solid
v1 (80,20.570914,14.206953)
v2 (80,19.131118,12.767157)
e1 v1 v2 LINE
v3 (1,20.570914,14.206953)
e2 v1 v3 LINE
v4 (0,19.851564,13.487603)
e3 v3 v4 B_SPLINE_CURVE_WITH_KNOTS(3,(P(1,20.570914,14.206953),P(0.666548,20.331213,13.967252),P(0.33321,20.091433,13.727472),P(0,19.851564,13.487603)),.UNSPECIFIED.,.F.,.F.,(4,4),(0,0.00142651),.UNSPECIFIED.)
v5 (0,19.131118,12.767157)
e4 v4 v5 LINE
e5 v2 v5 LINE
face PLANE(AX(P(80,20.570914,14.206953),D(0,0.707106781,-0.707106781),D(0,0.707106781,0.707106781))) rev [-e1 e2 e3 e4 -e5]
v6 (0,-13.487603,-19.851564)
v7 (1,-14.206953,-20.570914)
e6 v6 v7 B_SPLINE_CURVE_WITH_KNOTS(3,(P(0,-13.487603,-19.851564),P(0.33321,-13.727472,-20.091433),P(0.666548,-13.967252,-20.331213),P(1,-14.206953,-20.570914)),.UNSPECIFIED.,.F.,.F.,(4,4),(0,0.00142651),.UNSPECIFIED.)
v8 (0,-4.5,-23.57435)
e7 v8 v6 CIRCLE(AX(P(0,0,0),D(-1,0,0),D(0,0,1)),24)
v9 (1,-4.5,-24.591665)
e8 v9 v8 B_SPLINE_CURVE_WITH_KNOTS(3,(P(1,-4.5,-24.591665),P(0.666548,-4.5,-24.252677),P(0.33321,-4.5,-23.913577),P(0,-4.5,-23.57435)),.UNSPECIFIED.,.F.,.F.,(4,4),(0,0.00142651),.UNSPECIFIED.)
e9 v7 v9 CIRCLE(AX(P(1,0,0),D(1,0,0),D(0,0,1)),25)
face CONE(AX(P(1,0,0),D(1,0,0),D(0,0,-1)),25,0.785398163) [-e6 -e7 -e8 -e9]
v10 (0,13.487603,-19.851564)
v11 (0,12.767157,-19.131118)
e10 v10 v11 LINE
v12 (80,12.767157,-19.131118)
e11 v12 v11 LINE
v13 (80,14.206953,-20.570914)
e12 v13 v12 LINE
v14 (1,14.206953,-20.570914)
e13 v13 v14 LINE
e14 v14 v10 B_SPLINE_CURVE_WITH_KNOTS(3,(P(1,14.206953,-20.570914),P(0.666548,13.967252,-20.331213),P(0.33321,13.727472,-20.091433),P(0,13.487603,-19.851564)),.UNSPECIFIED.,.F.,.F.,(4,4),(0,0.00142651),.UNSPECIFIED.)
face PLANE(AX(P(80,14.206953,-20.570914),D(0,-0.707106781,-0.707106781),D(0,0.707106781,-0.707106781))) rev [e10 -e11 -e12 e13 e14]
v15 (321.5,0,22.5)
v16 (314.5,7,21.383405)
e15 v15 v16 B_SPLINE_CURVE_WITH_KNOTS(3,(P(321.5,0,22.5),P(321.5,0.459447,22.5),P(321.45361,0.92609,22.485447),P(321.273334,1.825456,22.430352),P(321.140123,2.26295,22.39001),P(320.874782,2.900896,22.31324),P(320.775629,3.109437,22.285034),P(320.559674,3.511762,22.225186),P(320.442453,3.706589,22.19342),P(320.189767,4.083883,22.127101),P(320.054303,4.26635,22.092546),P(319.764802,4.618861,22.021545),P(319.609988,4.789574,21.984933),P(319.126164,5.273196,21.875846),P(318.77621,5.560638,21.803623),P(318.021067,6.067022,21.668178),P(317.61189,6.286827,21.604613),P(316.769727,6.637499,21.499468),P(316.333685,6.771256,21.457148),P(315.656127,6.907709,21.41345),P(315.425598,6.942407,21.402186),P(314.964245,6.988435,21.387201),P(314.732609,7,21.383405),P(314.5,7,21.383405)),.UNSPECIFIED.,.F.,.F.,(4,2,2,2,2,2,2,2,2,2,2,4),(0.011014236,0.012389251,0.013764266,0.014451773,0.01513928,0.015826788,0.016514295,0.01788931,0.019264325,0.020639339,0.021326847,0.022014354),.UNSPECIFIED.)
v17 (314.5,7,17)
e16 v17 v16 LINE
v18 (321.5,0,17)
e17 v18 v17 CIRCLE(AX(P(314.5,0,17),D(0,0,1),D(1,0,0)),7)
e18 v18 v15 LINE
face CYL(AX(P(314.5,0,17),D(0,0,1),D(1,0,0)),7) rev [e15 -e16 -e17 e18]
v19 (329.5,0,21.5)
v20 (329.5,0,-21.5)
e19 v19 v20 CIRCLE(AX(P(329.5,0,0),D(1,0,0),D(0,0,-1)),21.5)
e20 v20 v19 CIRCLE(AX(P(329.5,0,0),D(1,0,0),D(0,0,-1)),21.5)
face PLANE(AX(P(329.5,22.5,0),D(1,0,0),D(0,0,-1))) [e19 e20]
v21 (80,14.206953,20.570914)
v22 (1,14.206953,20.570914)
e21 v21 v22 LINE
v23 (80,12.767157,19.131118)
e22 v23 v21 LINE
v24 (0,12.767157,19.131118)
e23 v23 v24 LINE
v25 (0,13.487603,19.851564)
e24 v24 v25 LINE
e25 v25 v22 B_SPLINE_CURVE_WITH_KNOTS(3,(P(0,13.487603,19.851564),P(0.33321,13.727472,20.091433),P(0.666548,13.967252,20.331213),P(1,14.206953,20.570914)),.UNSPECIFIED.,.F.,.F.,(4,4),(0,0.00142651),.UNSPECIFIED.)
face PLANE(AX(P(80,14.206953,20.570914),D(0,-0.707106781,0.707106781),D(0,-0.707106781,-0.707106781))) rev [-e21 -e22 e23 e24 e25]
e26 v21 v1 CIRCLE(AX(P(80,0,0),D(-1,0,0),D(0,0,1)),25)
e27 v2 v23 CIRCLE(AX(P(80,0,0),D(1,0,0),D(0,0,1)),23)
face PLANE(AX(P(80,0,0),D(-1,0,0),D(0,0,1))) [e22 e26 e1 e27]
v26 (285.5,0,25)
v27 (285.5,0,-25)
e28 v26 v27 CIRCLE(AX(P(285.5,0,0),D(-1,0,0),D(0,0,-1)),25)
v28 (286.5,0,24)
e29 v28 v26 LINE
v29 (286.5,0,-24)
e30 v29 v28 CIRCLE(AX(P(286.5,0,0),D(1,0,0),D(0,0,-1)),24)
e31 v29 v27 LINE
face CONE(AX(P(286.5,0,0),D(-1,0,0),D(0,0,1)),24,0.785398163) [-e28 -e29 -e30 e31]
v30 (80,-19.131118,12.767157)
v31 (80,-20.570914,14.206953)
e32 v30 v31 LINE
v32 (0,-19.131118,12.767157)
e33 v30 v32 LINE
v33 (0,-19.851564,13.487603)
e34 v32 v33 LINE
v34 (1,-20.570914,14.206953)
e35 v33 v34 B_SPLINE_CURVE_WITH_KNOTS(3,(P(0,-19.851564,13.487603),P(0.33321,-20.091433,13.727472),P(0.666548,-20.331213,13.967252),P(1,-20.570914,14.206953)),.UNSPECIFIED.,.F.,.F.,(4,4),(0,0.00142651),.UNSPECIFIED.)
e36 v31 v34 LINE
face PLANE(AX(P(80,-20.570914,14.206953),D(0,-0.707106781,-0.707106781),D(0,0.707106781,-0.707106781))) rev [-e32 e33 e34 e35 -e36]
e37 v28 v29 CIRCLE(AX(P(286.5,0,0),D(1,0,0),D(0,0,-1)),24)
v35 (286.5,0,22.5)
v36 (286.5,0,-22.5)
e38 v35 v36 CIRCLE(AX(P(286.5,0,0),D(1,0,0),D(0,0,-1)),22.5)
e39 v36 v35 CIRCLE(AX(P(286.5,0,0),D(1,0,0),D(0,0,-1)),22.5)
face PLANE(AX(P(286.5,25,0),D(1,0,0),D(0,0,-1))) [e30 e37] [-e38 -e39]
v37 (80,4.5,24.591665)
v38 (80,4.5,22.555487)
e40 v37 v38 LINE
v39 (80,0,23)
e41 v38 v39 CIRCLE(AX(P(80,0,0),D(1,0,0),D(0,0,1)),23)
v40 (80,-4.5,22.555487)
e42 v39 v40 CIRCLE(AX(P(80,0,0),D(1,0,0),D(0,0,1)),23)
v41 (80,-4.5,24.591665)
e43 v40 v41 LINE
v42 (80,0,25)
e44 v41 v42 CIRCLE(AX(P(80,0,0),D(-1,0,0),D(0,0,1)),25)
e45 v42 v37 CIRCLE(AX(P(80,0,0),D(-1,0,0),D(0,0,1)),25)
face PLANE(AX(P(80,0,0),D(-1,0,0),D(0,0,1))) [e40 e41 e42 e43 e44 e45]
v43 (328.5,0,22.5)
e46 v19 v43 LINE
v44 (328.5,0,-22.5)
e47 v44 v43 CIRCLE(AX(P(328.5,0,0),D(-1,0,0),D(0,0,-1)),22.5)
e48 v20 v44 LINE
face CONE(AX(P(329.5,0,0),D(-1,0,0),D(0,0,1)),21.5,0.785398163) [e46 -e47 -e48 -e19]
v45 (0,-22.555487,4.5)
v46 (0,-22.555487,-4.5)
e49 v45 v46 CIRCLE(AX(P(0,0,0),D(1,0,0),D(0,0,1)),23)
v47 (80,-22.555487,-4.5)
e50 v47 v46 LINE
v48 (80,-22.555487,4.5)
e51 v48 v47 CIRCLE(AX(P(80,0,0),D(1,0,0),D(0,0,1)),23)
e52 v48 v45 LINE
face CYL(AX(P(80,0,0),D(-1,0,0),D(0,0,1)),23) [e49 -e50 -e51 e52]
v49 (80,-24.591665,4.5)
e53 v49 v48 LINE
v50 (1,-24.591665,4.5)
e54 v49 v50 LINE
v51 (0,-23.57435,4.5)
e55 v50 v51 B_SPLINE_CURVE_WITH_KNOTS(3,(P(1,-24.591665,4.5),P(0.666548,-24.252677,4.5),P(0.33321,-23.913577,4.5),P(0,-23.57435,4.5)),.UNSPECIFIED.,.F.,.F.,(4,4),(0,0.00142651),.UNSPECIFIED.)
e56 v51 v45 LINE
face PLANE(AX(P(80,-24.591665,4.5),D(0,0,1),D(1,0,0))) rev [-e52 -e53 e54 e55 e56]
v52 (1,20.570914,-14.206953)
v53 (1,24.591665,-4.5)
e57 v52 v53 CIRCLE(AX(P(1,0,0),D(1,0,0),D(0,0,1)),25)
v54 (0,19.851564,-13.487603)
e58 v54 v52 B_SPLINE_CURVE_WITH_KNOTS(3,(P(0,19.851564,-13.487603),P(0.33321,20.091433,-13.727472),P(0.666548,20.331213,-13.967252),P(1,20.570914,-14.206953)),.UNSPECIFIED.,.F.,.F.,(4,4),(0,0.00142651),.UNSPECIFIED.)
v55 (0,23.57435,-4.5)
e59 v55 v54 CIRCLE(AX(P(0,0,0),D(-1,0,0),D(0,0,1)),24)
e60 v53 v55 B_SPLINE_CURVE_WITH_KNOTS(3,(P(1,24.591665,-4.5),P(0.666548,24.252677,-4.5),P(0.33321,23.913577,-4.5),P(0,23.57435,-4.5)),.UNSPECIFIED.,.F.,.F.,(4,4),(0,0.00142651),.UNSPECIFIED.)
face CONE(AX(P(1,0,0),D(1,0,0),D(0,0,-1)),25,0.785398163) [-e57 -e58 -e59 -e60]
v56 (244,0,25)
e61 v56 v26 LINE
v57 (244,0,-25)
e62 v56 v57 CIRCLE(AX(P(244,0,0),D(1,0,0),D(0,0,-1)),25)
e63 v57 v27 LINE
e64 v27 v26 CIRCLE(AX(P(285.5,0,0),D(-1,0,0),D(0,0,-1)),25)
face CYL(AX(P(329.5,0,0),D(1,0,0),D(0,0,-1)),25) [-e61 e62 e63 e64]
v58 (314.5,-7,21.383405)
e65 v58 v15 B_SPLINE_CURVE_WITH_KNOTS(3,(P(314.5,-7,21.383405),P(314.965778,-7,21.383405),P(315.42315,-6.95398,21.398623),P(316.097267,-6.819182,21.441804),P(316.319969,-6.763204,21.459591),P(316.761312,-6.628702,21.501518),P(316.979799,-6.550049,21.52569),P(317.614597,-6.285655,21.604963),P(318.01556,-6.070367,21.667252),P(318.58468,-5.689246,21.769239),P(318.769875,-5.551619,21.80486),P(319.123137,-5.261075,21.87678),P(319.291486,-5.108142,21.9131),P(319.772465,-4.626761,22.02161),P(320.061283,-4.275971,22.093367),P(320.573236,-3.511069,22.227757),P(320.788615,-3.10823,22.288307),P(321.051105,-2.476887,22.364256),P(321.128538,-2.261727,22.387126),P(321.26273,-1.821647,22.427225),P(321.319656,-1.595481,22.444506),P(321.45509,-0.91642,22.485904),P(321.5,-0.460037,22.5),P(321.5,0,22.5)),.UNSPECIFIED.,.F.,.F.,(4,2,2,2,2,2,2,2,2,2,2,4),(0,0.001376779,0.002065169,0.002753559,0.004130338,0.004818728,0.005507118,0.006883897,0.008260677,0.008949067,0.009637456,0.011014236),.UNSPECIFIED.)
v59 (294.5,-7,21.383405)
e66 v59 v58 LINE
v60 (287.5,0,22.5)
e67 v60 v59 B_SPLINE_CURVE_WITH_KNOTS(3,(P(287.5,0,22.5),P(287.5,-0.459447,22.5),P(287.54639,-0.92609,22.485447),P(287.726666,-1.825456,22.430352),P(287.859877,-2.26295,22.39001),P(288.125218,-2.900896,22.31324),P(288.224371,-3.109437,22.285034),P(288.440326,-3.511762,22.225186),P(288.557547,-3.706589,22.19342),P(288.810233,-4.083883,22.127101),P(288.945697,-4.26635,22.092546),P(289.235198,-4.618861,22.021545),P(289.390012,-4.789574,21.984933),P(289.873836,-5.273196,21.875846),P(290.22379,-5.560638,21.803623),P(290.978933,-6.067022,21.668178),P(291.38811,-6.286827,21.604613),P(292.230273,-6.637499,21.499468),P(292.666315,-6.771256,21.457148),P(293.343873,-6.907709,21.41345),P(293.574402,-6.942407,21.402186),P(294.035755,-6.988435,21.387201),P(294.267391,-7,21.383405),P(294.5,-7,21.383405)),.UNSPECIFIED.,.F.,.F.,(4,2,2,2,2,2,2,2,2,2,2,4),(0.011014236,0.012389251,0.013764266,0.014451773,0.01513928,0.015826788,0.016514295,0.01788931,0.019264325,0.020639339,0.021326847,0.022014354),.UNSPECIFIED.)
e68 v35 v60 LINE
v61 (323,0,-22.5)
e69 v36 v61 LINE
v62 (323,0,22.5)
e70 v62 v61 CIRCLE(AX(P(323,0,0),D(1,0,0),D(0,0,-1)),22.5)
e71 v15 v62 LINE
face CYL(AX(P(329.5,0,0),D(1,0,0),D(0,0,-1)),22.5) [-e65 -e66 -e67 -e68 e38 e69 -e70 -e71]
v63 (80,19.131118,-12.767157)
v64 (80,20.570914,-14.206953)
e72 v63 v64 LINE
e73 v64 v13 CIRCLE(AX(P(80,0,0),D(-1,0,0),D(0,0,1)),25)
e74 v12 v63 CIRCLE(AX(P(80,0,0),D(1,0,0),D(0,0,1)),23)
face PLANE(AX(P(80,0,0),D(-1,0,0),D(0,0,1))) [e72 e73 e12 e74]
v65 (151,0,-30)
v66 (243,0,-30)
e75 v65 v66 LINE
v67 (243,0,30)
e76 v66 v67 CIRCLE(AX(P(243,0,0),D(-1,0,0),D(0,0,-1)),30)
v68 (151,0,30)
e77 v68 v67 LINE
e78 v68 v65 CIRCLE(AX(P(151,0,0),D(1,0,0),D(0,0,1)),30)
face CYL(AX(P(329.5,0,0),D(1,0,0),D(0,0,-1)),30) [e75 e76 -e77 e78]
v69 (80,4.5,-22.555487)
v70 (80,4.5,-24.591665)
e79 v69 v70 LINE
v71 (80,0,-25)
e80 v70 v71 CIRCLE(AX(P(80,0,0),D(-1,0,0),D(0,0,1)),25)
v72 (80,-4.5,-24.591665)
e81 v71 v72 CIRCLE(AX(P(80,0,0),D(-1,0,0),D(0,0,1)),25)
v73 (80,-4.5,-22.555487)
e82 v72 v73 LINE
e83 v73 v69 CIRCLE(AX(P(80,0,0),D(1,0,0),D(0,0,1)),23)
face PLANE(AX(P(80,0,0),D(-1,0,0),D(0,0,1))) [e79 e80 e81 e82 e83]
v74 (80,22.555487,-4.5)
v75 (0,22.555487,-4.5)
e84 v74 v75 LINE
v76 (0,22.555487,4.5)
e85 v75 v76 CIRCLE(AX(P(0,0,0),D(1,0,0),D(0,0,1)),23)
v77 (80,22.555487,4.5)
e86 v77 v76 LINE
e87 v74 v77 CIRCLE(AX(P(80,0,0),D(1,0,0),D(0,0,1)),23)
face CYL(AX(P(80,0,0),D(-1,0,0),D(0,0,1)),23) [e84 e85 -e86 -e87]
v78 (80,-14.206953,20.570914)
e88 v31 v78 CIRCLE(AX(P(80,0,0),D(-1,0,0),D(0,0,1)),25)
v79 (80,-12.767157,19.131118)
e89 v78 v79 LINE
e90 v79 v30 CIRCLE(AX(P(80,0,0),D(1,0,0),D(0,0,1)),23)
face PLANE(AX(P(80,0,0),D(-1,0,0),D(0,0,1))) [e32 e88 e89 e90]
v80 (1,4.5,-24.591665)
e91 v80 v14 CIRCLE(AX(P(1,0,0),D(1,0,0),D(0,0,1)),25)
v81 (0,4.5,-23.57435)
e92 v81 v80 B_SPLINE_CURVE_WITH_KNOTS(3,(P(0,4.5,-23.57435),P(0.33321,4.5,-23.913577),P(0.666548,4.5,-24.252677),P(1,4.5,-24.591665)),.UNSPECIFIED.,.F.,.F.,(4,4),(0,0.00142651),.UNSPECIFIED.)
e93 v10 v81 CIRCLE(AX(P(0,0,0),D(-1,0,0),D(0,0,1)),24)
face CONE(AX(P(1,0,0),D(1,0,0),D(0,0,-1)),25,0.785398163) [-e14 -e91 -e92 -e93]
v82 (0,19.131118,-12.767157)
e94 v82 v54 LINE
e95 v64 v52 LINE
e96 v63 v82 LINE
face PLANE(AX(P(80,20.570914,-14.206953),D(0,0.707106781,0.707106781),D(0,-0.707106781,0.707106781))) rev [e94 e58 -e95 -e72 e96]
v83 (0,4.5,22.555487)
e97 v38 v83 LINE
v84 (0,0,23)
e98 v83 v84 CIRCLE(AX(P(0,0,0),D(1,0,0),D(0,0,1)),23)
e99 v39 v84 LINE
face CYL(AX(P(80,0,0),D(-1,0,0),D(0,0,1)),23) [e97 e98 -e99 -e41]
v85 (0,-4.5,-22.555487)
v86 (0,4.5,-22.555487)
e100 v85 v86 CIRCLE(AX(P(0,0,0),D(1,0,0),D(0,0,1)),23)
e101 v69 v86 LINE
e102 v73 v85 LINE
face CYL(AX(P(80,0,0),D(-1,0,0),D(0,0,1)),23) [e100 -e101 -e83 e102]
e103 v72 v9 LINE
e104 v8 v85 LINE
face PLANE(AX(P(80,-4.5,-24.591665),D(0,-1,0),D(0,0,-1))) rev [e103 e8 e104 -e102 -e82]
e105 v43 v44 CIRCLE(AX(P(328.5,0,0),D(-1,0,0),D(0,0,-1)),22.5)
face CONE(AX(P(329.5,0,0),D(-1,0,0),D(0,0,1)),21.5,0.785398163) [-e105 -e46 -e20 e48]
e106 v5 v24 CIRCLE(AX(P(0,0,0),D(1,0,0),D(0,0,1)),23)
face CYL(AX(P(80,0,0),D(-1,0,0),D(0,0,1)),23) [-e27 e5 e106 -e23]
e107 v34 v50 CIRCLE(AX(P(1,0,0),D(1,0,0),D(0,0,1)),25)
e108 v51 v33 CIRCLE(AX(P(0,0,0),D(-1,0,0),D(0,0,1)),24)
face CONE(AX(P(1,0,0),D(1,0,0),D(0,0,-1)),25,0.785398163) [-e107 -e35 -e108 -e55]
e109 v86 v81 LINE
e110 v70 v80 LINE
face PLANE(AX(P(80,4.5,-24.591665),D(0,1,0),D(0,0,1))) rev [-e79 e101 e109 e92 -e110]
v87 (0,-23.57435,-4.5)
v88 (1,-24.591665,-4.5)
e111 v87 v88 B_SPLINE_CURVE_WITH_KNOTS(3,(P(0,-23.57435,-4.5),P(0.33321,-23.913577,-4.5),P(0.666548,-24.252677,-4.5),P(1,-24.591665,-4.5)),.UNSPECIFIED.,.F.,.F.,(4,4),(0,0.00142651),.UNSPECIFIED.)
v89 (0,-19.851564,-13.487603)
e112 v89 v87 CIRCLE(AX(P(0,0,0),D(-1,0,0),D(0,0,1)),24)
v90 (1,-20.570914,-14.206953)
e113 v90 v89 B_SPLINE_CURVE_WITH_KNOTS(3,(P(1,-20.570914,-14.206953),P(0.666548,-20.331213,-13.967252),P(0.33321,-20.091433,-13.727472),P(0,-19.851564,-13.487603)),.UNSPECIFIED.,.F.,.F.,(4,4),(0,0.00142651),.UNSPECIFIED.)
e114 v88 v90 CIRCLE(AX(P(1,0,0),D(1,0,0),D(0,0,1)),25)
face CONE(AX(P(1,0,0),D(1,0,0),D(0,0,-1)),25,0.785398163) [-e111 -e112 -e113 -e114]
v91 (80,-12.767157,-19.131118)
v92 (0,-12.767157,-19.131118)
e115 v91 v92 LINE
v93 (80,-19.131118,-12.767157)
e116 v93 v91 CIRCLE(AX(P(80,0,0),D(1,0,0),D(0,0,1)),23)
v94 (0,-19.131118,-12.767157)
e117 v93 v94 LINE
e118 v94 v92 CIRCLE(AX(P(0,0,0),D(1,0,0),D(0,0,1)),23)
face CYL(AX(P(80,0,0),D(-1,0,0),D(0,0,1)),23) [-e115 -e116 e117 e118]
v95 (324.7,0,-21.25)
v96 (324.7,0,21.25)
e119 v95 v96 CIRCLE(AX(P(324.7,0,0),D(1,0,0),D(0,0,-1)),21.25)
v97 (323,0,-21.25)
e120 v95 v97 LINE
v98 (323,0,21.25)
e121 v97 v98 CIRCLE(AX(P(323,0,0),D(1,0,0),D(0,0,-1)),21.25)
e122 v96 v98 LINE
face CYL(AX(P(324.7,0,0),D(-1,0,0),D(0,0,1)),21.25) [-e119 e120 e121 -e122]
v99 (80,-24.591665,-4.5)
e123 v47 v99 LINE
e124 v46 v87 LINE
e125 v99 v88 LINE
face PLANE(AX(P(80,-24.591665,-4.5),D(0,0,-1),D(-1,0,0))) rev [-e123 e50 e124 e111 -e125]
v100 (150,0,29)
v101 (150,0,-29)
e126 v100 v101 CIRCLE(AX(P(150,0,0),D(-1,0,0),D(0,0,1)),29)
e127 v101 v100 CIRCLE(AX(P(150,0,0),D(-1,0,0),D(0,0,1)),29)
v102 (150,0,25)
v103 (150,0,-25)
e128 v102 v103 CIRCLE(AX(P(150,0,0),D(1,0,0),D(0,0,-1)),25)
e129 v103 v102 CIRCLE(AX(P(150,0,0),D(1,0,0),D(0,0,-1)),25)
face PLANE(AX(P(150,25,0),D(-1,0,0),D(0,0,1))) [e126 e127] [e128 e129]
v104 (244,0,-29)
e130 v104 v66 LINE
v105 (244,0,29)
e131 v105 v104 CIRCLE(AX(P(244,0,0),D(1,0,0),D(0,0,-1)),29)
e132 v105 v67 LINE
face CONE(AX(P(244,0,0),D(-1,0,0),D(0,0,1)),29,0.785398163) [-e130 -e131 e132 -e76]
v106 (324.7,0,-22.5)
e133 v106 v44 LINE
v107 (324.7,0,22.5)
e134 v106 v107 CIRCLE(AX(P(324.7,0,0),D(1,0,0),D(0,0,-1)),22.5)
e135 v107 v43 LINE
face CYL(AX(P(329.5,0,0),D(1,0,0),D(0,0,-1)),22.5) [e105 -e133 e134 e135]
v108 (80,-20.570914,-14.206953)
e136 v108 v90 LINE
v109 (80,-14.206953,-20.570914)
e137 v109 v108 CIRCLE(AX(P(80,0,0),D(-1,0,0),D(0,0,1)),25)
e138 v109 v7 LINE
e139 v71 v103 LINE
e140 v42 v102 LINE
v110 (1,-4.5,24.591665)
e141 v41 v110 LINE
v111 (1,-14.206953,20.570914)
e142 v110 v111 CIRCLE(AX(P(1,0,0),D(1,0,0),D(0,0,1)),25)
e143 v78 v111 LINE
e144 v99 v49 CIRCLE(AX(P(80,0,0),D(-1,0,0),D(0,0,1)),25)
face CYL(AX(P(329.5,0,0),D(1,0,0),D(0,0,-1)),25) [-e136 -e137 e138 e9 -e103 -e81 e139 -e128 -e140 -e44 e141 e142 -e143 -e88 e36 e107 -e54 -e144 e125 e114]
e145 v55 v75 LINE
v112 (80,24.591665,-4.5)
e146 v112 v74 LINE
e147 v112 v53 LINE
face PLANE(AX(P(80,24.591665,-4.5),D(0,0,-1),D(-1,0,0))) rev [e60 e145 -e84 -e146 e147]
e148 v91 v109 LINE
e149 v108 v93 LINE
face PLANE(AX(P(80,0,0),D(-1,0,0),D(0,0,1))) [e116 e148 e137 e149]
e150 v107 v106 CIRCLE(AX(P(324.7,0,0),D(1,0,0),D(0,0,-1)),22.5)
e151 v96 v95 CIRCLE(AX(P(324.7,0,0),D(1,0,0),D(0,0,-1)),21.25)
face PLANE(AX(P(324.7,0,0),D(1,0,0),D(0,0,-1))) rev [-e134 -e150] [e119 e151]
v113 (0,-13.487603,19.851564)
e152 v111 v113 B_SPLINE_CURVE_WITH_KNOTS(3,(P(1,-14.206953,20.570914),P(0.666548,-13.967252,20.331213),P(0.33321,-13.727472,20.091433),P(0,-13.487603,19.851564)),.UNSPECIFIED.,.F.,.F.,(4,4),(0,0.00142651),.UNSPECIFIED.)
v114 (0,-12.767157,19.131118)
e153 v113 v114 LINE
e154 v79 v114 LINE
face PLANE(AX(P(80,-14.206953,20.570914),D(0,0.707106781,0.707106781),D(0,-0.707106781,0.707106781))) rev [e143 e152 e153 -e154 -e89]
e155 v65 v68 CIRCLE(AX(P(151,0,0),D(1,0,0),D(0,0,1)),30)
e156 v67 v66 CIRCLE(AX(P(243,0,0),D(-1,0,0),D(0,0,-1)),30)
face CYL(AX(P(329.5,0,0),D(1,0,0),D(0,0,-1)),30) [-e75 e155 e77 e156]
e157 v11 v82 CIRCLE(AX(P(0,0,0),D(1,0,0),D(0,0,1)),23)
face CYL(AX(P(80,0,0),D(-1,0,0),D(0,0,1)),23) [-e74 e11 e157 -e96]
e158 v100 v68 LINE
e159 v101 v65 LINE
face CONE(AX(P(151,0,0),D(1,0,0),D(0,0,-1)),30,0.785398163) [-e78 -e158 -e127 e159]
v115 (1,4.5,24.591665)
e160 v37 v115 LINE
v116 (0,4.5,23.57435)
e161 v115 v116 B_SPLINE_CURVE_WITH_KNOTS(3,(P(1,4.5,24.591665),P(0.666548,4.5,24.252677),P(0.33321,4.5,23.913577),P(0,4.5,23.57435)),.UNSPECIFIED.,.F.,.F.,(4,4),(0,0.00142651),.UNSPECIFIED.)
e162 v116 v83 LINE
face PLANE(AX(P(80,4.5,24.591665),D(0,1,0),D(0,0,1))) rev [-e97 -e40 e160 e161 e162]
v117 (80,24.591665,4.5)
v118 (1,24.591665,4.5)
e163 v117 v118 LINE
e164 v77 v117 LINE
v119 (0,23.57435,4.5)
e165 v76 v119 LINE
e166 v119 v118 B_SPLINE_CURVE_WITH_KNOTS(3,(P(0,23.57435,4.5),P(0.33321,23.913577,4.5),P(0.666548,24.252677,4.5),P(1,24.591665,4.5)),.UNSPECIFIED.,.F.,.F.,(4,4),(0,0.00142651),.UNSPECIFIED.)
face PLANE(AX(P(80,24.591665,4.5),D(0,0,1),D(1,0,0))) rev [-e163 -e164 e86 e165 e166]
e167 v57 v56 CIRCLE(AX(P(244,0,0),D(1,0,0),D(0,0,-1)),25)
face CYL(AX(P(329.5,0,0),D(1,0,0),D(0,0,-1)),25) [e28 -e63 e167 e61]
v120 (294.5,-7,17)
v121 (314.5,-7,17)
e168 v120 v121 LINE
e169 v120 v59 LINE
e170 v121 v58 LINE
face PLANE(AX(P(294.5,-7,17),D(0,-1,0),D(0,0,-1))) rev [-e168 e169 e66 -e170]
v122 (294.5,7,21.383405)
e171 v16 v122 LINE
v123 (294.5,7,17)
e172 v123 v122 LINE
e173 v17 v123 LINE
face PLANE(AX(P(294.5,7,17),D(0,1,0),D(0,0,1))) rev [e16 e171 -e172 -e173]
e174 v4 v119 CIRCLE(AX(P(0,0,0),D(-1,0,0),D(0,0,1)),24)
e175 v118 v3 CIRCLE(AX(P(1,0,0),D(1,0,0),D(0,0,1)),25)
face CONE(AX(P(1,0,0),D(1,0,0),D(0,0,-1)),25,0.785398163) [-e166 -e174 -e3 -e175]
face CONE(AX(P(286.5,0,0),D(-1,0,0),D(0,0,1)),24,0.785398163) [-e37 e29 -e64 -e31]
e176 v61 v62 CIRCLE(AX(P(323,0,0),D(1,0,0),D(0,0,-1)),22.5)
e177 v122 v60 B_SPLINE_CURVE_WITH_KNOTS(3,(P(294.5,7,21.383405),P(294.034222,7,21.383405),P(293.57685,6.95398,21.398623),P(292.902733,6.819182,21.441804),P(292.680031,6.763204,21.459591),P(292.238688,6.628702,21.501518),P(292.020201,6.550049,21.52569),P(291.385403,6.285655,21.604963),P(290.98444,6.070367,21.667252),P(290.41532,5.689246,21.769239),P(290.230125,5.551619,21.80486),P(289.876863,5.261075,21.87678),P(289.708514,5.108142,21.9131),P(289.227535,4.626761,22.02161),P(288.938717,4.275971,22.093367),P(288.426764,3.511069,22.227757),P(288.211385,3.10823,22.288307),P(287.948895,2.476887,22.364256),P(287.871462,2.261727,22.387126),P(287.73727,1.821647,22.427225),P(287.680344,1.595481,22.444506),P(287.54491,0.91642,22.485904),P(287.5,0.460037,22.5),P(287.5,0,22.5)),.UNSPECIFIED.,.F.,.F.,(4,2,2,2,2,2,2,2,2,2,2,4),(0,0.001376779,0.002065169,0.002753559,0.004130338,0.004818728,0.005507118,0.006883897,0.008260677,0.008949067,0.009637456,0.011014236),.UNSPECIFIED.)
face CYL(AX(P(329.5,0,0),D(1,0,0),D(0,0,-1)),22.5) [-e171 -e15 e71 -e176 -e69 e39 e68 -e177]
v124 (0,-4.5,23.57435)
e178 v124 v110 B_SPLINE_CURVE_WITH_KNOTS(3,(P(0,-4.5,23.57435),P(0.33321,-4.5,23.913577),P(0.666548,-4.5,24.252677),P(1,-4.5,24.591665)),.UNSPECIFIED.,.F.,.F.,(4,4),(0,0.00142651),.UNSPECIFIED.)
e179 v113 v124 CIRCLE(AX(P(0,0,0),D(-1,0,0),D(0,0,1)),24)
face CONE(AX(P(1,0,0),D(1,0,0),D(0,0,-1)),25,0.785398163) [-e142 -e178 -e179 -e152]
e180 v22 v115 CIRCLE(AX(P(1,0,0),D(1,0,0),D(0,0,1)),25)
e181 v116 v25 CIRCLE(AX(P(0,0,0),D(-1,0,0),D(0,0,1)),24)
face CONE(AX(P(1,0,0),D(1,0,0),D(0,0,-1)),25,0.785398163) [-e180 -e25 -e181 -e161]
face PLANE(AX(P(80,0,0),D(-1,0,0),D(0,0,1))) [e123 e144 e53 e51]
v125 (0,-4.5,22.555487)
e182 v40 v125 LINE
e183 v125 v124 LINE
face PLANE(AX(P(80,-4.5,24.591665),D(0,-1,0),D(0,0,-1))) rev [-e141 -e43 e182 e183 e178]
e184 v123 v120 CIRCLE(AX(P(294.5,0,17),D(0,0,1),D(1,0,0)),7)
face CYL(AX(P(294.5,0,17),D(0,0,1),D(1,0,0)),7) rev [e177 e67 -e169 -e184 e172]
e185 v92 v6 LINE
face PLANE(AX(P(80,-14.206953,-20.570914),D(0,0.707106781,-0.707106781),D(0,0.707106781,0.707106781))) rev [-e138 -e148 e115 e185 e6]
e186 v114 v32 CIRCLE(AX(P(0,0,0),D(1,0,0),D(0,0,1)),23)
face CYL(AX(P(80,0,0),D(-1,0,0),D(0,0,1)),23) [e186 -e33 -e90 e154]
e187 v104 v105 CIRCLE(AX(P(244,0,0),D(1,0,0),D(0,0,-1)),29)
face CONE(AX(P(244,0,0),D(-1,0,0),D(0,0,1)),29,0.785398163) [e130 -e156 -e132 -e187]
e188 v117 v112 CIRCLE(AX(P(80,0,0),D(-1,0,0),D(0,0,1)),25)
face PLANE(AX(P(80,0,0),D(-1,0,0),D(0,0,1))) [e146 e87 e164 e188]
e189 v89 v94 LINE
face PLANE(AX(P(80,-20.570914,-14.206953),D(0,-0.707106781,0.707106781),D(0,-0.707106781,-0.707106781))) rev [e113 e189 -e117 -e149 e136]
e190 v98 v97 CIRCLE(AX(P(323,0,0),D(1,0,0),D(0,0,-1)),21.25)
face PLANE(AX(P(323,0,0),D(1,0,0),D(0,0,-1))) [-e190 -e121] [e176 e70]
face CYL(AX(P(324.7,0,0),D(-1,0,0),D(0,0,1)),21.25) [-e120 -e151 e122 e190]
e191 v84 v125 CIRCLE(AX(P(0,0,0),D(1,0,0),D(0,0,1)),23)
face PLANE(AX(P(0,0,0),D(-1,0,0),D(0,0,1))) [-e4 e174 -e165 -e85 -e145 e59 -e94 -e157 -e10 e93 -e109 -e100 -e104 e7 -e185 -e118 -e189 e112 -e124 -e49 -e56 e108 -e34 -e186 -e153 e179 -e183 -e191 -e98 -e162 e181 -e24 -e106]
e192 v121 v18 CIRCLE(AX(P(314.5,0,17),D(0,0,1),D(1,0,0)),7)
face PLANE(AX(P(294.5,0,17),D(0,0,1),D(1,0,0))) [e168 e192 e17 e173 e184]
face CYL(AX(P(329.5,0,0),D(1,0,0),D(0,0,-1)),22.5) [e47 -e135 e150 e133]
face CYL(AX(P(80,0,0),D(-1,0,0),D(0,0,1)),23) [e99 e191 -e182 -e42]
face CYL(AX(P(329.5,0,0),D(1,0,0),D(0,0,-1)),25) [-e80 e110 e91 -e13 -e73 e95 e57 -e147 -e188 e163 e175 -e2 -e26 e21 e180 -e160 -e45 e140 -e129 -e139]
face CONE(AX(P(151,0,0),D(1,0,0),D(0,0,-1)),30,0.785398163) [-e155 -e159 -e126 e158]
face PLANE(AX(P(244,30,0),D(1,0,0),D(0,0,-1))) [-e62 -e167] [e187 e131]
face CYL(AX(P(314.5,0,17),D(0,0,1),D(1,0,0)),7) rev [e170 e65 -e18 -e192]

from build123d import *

# Parameters (mm, degrees)
CHAMFER_1_SIZE      = 1
CUT_EXTRUDE_START   = 1.7
SKETCH_2_R          = 22.5
SKETCH_2_R_2        = 21.25
CUT_EXTRUDE_1_DEPTH = 1.7
CUT_EXTRUDE_2_DEPTH = 5.5
CUT_EXTRUDE_START_2 = -80
CUT_EXTRUDE_3_DEPTH = 80
CHAMFER_2_SIZE      = 1


with BuildPart() as part:
    # 草图1 → 旋转1 (revolve)
    with BuildSketch(Plane.XY, mode=Mode.PRIVATE) as revolve_1_sk:
        Polygon((0, 0), (0, 25), (150, 25), (150, 30), (244, 30), (244, 25), (286.5, 25), (286.5, 22.5), (329.5, 22.5), (329.5, 0), align=None)
    revolve(revolve_1_sk.sketch.rotate(Axis((329.5, 0, 0), (-1, 0, 0)), 90), axis=Axis((329.5, 0, 0), (-1, 0, 0)))

    # 倒角1
    chamfer_1_edges = [part.edges().sort_by_distance(p)[0] for p in [
        (329.5, 0, 22.5),
        (286.5, 0, 25),
        (244, 0, 30),
        (150, 0, 30),
    ]]
    chamfer(chamfer_1_edges, length=CHAMFER_1_SIZE)

    # 草图2 → 切除-拉伸1 (cut)
    with BuildSketch(Plane(origin=(323, 0, 0), x_dir=(0, 0, -1), z_dir=(1, 0, 0)).offset(CUT_EXTRUDE_START)):
        Circle(SKETCH_2_R)
        Circle(SKETCH_2_R_2, mode=Mode.SUBTRACT)
    extrude(amount=-CUT_EXTRUDE_1_DEPTH, mode=Mode.SUBTRACT)

    # 草图3 → 切除-拉伸2 (cut)
    with BuildSketch(Plane.XY.offset(22.5)):
        with BuildLine():
            Line((294.5, 7), (314.5, 7))
            ThreePointArc((314.5, 7), (321.5, 0), (314.5, -7))
            Line((314.5, -7), (294.5, -7))
            ThreePointArc((294.5, -7), (287.5, 0), (294.5, 7))
        make_face()
    extrude(amount=-CUT_EXTRUDE_2_DEPTH, mode=Mode.SUBTRACT)

    # 草图4 → 切除-拉伸3 (cut)
    with BuildSketch(Plane.ZY.offset(CUT_EXTRUDE_START_2)):
        with BuildLine():
            Line((-4.5, 24.591665255), (-4.5, 22.555487137))
            ThreePointArc((-4.5, 22.555487137), (0, 23), (4.5, 22.555487137))
            Line((4.5, 22.555487137), (4.5, 24.591665255))
            ThreePointArc((4.5, 24.591665255), (0, 25), (-4.5, 24.591665255))
        make_face()
        with BuildLine():
            Line((20.570913778, 14.206952747), (19.131118423, 12.767157392))
            ThreePointArc((19.131118423, 12.767157392), (16.263455967, 16.263455967), (12.767157392, 19.131118423))
            Line((12.767157392, 19.131118423), (14.206952747, 20.570913778))
            ThreePointArc((14.206952747, 20.570913778), (17.67766953, 17.67766953), (20.570913778, 14.206952747))
        make_face()
        with BuildLine():
            Line((24.591665255, -4.5), (22.555487137, -4.5))
            ThreePointArc((22.555487137, -4.5), (23, 0), (22.555487137, 4.5))
            Line((22.555487137, 4.5), (24.591665255, 4.5))
            ThreePointArc((24.591665255, 4.5), (25, 0), (24.591665255, -4.5))
        make_face()
        with BuildLine():
            Line((14.206952747, -20.570913778), (12.767157392, -19.131118423))
            ThreePointArc((12.767157392, -19.131118423), (16.263455967, -16.263455967), (19.131118423, -12.767157392))
            Line((19.131118423, -12.767157392), (20.570913778, -14.206952747))
            ThreePointArc((20.570913778, -14.206952747), (17.67766953, -17.67766953), (14.206952747, -20.570913778))
        make_face()
        with BuildLine():
            Line((-4.5, -24.591665255), (-4.5, -22.555487137))
            ThreePointArc((-4.5, -22.555487137), (0, -23), (4.5, -22.555487137))
            Line((4.5, -22.555487137), (4.5, -24.591665255))
            ThreePointArc((4.5, -24.591665255), (0, -25), (-4.5, -24.591665255))
        make_face()
        with BuildLine():
            Line((-20.570913778, -14.206952747), (-19.131118423, -12.767157392))
            ThreePointArc((-19.131118423, -12.767157392), (-16.263455967, -16.263455967), (-12.767157392, -19.131118423))
            Line((-12.767157392, -19.131118423), (-14.206952747, -20.570913778))
            ThreePointArc((-14.206952747, -20.570913778), (-17.67766953, -17.67766953), (-20.570913778, -14.206952747))
        make_face()
        with BuildLine():
            Line((-24.591665255, 4.5), (-22.555487137, 4.5))
            ThreePointArc((-22.555487137, 4.5), (-23, 0), (-22.555487137, -4.5))
            Line((-22.555487137, -4.5), (-24.591665255, -4.5))
            ThreePointArc((-24.591665255, -4.5), (-25, 0), (-24.591665255, 4.5))
        make_face()
        with BuildLine():
            Line((-14.206952747, 20.570913778), (-12.767157392, 19.131118423))
            ThreePointArc((-12.767157392, 19.131118423), (-16.263455967, 16.263455967), (-19.131118423, 12.767157392))
            Line((-19.131118423, 12.767157392), (-20.570913778, 14.206952747))
            ThreePointArc((-20.570913778, 14.206952747), (-17.67766953, 17.67766953), (-14.206952747, 20.570913778))
        make_face()
    extrude(amount=CUT_EXTRUDE_3_DEPTH, mode=Mode.SUBTRACT)

    # 倒角2
    chamfer_2_edges = [part.edges().sort_by_distance(p)[0] for p in [
        (0, 23.096988313, 9.567085809),
        (0, 9.567085809, 23.096988313),
        (0, -9.567085809, 23.096988313),
        (0, -23.096988313, 9.567085809),
        (0, -23.096988313, -9.567085809),
        (0, -9.567085809, -23.096988313),
        (0, 9.567085809, -23.096988313),
        (0, 23.096988313, -9.567085809),
    ]]
    chamfer(chamfer_2_edges, length=CHAMFER_2_SIZE)


solid = part.part
